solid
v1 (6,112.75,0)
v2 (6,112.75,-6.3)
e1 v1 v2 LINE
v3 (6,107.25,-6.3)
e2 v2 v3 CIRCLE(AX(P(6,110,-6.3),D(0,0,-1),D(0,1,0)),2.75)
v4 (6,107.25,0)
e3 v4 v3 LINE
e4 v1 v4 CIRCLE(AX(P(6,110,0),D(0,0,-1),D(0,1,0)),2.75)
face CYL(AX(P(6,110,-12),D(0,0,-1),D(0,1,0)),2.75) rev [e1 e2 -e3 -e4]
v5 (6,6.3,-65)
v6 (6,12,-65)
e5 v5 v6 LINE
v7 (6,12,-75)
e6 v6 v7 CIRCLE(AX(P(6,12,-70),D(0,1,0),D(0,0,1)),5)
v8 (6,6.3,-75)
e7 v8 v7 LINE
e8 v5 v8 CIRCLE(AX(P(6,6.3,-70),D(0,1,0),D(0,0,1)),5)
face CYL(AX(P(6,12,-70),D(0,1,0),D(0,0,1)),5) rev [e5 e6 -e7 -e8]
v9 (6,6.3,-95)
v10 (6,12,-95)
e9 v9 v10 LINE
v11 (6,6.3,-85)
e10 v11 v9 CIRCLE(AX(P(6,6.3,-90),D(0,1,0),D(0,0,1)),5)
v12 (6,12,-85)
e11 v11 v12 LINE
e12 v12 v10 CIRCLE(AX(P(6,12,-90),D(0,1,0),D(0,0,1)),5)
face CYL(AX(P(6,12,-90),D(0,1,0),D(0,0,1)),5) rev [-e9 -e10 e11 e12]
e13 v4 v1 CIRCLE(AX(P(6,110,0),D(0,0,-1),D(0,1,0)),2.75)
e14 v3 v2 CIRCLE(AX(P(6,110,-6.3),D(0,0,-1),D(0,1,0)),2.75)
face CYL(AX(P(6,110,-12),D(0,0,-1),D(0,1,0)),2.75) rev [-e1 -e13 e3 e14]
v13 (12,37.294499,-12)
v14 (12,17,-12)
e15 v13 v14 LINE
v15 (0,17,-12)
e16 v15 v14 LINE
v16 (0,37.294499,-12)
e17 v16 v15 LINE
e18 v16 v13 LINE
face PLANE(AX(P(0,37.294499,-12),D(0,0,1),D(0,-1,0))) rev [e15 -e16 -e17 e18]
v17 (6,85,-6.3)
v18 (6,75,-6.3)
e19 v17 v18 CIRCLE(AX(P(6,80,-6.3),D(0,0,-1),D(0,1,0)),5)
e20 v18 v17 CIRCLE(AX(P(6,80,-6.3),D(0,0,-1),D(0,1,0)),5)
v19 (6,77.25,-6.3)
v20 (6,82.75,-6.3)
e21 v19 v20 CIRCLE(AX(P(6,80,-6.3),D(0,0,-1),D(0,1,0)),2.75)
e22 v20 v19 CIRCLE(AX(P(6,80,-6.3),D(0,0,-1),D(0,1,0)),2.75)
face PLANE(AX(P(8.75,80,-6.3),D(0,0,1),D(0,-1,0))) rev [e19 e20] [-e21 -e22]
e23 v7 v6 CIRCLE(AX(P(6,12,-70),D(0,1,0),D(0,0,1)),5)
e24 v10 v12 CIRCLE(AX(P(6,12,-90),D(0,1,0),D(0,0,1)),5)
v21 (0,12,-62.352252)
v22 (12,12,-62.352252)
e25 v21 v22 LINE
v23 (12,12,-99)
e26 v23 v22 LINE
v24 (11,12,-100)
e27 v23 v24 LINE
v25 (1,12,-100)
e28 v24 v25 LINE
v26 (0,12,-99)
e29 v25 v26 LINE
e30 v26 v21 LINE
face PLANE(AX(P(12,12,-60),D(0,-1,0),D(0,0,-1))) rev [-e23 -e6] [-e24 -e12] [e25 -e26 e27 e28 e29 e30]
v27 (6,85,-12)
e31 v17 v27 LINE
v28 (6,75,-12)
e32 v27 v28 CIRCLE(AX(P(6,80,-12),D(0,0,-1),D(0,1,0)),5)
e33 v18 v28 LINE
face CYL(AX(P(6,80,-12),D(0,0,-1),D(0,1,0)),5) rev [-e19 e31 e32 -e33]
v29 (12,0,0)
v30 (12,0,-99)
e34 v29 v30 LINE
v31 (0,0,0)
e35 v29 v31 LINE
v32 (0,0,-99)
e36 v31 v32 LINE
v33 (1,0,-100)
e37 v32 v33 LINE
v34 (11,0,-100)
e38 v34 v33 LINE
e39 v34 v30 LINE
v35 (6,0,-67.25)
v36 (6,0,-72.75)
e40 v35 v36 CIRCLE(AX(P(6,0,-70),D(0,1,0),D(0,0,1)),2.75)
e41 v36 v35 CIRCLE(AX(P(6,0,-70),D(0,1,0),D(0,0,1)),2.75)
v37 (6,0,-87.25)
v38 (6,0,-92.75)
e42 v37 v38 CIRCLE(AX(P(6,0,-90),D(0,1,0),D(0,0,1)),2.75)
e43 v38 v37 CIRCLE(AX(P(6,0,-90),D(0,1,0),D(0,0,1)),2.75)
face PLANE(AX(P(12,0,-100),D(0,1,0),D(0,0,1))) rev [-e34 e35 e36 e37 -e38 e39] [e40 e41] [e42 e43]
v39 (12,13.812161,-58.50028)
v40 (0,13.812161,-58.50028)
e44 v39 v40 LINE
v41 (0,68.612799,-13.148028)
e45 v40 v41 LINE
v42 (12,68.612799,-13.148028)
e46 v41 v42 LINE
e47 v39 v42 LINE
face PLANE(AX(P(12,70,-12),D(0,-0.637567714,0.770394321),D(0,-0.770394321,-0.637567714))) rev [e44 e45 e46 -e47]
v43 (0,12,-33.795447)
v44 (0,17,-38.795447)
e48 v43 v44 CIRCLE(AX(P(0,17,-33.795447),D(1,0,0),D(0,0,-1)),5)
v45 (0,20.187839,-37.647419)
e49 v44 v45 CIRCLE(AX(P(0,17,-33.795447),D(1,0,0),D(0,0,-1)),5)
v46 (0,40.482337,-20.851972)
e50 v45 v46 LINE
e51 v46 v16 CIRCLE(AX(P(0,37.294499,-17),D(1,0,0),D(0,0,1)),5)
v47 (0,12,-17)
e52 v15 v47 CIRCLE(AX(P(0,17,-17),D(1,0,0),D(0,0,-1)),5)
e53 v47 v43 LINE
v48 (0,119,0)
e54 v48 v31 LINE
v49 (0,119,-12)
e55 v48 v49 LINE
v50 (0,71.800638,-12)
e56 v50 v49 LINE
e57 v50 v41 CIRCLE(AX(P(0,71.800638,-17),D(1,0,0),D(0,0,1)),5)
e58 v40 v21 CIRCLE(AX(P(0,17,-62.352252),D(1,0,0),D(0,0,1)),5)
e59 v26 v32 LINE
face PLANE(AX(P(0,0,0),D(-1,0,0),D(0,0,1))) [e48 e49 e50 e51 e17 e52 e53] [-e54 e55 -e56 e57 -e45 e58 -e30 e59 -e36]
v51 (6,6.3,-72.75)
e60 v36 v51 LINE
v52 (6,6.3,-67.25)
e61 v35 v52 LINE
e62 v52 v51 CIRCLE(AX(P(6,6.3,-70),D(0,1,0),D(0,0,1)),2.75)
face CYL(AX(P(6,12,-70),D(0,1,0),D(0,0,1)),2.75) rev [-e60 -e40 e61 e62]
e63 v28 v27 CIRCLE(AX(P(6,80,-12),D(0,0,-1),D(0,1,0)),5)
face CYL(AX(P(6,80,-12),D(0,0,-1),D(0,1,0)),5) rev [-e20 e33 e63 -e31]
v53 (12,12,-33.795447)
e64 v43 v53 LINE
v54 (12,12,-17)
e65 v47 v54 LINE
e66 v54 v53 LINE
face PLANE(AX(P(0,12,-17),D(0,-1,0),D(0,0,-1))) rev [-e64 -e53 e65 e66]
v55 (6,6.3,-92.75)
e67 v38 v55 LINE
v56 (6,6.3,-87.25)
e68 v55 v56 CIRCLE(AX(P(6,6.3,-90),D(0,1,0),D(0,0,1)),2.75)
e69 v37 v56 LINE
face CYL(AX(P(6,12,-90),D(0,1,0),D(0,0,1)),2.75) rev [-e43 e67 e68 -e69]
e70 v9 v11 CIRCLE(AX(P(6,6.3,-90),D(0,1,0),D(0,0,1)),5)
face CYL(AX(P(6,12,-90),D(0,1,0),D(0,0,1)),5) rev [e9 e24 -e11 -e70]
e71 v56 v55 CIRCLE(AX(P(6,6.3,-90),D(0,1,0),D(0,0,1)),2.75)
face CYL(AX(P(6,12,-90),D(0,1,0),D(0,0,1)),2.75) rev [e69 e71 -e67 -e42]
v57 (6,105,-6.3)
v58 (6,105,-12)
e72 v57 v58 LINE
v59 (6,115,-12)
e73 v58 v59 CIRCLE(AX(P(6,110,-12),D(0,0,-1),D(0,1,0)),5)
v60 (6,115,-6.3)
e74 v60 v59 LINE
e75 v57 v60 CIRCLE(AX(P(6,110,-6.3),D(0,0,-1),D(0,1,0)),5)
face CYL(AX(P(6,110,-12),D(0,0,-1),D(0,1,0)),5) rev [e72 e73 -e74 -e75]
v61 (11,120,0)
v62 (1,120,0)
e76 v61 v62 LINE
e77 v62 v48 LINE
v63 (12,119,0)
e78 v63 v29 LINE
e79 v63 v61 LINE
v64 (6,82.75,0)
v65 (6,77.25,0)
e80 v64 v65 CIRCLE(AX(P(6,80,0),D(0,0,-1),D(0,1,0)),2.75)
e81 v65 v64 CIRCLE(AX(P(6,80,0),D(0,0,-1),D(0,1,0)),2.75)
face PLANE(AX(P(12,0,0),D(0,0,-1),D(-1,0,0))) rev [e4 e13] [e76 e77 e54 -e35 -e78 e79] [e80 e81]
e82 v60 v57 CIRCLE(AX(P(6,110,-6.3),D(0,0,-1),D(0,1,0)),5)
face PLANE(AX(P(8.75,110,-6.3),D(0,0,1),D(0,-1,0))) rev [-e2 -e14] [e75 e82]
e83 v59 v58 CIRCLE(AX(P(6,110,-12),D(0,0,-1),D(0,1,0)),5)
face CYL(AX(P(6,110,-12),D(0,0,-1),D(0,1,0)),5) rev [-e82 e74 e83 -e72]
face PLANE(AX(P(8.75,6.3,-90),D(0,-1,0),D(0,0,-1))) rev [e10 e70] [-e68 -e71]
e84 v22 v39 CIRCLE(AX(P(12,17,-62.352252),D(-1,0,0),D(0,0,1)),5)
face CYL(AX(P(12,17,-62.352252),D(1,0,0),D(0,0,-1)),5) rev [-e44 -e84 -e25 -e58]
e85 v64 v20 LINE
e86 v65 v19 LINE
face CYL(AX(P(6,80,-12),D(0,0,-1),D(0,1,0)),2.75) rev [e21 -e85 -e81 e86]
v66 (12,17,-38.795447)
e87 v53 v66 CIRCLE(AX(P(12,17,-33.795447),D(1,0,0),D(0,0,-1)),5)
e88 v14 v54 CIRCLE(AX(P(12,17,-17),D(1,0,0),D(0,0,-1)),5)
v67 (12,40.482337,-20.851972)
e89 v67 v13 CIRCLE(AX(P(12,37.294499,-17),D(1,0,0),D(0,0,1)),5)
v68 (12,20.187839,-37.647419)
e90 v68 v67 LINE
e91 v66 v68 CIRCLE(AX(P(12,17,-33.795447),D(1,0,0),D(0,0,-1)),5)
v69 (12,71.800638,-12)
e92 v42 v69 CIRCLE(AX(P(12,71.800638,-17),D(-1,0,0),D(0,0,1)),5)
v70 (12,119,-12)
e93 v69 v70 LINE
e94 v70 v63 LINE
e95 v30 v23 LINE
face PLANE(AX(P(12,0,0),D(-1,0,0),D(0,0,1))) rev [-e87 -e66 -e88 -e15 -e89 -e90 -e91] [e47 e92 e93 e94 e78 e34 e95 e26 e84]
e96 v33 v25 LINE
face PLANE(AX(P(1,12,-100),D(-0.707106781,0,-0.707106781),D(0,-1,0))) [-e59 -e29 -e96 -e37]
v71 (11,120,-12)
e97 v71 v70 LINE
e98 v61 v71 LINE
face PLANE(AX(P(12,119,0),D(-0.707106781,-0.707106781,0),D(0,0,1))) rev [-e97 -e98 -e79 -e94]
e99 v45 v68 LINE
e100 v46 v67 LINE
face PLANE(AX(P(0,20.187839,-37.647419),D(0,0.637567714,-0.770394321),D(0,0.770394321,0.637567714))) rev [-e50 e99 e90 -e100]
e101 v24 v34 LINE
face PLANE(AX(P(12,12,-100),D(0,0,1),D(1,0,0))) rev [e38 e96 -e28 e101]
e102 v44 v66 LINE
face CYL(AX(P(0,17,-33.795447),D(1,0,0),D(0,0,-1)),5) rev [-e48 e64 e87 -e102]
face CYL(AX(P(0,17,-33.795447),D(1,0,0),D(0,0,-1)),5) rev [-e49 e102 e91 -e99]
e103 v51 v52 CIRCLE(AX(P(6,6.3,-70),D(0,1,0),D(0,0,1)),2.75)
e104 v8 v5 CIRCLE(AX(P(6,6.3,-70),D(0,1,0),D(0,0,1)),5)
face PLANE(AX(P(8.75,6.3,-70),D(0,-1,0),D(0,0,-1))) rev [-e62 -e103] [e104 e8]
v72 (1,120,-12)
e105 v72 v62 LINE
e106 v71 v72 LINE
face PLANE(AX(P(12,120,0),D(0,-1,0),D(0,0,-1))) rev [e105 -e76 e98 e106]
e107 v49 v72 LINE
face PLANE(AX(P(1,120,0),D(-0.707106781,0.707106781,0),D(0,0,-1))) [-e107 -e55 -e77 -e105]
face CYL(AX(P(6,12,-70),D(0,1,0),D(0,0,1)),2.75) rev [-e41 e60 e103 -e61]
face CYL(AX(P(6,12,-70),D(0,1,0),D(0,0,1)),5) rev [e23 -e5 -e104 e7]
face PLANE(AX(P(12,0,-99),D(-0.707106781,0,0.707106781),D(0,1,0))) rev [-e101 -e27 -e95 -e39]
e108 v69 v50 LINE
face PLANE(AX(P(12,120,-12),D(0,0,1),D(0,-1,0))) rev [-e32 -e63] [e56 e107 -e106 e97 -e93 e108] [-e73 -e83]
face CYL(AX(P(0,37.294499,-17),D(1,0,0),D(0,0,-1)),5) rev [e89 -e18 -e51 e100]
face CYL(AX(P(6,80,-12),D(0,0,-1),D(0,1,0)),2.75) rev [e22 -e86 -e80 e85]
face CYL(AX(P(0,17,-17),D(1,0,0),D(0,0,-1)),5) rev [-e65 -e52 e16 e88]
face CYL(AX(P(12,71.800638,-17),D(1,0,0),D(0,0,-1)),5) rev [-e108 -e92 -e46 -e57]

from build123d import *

# Parameters (mm, degrees)
BOSS_EXTRUDE1_DEPTH                                  = 12
CUT_EXTRUDE1_DEPTH                                   = 157.665248221
CBORE_FOR_M5_HEXAGON_SOCKET_HEAD_CAP_SCR_D           = 5.5
CBORE_FOR_M5_HEXAGON_SOCKET_HEAD_CAP_SCR_CBORE_D     = 10
CBORE_FOR_M5_HEXAGON_SOCKET_HEAD_CAP_SCR_CBORE_DEPTH = 5.7
CBORE_FOR_M5_HEXAGON_SOCKET_HEAD_CAP_2_D             = 5.5
CBORE_FOR_M5_HEXAGON_SOCKET_HEAD_CAP_2_CBORE_D       = 10
CBORE_FOR_M5_HEXAGON_SOCKET_HEAD_CAP_2_CBORE_DEPTH   = 5.7
CHAMFER1_SIZE                                        = 1
FILLET1_R                                            = 5


with BuildPart() as part:
    # Sketch1 → Boss-Extrude1 (new body)
    with BuildSketch(Plane(origin=(0, 0, 0), x_dir=(0, 0, -1), z_dir=(1, 0, 0))):
        Polygon((0, 0), (0, 120), (12, 120), (12, 70), (60, 12), (100, 12), (100, 0), align=None)
    extrude(amount=BOSS_EXTRUDE1_DEPTH)

    # Sketch2 → Cut-Extrude1 (cut, through all)
    with BuildSketch(Plane(origin=(12, 0, 0), x_dir=(0, 0, -1), z_dir=(1, 0, 0))):
        with BuildLine():
            Line((12, 37.294498848), (12, 17))
            ThreePointArc((12, 17), (13.464466094, 13.464466094), (17, 12))
            Line((17, 12), (33.795447323, 12))
            ThreePointArc((33.795447323, 12), (38.319781133, 14.871525529), (37.647418928, 20.18783857))
            Line((37.647418928, 20.18783857), (20.851971606, 40.482337418))
            ThreePointArc((20.851971606, 40.482337418), (15.305871615, 41.998744698), (12, 37.294498848))
        make_face()
    extrude(amount=-CUT_EXTRUDE1_DEPTH, mode=Mode.SUBTRACT)

    # CBORE for M5 Hexagon socket head cap scr (through all)
    with Locations(Plane(origin=(0, 0, -12), x_dir=(-1, 0, 0), z_dir=(0, 0, -1))):
        with Locations((-6, 80), (-6, 110)):
            CounterBoreHole(CBORE_FOR_M5_HEXAGON_SOCKET_HEAD_CAP_SCR_D / 2, CBORE_FOR_M5_HEXAGON_SOCKET_HEAD_CAP_SCR_CBORE_D / 2, CBORE_FOR_M5_HEXAGON_SOCKET_HEAD_CAP_SCR_CBORE_DEPTH)

    # CBORE for M5 Hexagon socket head cap 2 (through all)
    with Locations(Plane(origin=(0, 12, 0), x_dir=(1, 0, 0), z_dir=(0, 1, 0))):
        with Locations((6, 70), (6, 90)):
            CounterBoreHole(CBORE_FOR_M5_HEXAGON_SOCKET_HEAD_CAP_2_D / 2, CBORE_FOR_M5_HEXAGON_SOCKET_HEAD_CAP_2_CBORE_D / 2, CBORE_FOR_M5_HEXAGON_SOCKET_HEAD_CAP_2_CBORE_DEPTH)

    # Chamfer1
    chamfer1_edges = [part.edges().sort_by_distance(p)[0] for p in [
        (12, 120, -6),
        (0, 120, -6),
        (12, 6, -100),
        (0, 6, -100),
    ]]
    chamfer(chamfer1_edges, length=CHAMFER1_SIZE)

    # Fillet1
    fillet1_edges = [part.edges().sort_by_distance(p)[0] for p in [
        (6, 70, -12),
        (6, 12, -60),
    ]]
    fillet(fillet1_edges, radius=FILLET1_R)


solid = part.part
